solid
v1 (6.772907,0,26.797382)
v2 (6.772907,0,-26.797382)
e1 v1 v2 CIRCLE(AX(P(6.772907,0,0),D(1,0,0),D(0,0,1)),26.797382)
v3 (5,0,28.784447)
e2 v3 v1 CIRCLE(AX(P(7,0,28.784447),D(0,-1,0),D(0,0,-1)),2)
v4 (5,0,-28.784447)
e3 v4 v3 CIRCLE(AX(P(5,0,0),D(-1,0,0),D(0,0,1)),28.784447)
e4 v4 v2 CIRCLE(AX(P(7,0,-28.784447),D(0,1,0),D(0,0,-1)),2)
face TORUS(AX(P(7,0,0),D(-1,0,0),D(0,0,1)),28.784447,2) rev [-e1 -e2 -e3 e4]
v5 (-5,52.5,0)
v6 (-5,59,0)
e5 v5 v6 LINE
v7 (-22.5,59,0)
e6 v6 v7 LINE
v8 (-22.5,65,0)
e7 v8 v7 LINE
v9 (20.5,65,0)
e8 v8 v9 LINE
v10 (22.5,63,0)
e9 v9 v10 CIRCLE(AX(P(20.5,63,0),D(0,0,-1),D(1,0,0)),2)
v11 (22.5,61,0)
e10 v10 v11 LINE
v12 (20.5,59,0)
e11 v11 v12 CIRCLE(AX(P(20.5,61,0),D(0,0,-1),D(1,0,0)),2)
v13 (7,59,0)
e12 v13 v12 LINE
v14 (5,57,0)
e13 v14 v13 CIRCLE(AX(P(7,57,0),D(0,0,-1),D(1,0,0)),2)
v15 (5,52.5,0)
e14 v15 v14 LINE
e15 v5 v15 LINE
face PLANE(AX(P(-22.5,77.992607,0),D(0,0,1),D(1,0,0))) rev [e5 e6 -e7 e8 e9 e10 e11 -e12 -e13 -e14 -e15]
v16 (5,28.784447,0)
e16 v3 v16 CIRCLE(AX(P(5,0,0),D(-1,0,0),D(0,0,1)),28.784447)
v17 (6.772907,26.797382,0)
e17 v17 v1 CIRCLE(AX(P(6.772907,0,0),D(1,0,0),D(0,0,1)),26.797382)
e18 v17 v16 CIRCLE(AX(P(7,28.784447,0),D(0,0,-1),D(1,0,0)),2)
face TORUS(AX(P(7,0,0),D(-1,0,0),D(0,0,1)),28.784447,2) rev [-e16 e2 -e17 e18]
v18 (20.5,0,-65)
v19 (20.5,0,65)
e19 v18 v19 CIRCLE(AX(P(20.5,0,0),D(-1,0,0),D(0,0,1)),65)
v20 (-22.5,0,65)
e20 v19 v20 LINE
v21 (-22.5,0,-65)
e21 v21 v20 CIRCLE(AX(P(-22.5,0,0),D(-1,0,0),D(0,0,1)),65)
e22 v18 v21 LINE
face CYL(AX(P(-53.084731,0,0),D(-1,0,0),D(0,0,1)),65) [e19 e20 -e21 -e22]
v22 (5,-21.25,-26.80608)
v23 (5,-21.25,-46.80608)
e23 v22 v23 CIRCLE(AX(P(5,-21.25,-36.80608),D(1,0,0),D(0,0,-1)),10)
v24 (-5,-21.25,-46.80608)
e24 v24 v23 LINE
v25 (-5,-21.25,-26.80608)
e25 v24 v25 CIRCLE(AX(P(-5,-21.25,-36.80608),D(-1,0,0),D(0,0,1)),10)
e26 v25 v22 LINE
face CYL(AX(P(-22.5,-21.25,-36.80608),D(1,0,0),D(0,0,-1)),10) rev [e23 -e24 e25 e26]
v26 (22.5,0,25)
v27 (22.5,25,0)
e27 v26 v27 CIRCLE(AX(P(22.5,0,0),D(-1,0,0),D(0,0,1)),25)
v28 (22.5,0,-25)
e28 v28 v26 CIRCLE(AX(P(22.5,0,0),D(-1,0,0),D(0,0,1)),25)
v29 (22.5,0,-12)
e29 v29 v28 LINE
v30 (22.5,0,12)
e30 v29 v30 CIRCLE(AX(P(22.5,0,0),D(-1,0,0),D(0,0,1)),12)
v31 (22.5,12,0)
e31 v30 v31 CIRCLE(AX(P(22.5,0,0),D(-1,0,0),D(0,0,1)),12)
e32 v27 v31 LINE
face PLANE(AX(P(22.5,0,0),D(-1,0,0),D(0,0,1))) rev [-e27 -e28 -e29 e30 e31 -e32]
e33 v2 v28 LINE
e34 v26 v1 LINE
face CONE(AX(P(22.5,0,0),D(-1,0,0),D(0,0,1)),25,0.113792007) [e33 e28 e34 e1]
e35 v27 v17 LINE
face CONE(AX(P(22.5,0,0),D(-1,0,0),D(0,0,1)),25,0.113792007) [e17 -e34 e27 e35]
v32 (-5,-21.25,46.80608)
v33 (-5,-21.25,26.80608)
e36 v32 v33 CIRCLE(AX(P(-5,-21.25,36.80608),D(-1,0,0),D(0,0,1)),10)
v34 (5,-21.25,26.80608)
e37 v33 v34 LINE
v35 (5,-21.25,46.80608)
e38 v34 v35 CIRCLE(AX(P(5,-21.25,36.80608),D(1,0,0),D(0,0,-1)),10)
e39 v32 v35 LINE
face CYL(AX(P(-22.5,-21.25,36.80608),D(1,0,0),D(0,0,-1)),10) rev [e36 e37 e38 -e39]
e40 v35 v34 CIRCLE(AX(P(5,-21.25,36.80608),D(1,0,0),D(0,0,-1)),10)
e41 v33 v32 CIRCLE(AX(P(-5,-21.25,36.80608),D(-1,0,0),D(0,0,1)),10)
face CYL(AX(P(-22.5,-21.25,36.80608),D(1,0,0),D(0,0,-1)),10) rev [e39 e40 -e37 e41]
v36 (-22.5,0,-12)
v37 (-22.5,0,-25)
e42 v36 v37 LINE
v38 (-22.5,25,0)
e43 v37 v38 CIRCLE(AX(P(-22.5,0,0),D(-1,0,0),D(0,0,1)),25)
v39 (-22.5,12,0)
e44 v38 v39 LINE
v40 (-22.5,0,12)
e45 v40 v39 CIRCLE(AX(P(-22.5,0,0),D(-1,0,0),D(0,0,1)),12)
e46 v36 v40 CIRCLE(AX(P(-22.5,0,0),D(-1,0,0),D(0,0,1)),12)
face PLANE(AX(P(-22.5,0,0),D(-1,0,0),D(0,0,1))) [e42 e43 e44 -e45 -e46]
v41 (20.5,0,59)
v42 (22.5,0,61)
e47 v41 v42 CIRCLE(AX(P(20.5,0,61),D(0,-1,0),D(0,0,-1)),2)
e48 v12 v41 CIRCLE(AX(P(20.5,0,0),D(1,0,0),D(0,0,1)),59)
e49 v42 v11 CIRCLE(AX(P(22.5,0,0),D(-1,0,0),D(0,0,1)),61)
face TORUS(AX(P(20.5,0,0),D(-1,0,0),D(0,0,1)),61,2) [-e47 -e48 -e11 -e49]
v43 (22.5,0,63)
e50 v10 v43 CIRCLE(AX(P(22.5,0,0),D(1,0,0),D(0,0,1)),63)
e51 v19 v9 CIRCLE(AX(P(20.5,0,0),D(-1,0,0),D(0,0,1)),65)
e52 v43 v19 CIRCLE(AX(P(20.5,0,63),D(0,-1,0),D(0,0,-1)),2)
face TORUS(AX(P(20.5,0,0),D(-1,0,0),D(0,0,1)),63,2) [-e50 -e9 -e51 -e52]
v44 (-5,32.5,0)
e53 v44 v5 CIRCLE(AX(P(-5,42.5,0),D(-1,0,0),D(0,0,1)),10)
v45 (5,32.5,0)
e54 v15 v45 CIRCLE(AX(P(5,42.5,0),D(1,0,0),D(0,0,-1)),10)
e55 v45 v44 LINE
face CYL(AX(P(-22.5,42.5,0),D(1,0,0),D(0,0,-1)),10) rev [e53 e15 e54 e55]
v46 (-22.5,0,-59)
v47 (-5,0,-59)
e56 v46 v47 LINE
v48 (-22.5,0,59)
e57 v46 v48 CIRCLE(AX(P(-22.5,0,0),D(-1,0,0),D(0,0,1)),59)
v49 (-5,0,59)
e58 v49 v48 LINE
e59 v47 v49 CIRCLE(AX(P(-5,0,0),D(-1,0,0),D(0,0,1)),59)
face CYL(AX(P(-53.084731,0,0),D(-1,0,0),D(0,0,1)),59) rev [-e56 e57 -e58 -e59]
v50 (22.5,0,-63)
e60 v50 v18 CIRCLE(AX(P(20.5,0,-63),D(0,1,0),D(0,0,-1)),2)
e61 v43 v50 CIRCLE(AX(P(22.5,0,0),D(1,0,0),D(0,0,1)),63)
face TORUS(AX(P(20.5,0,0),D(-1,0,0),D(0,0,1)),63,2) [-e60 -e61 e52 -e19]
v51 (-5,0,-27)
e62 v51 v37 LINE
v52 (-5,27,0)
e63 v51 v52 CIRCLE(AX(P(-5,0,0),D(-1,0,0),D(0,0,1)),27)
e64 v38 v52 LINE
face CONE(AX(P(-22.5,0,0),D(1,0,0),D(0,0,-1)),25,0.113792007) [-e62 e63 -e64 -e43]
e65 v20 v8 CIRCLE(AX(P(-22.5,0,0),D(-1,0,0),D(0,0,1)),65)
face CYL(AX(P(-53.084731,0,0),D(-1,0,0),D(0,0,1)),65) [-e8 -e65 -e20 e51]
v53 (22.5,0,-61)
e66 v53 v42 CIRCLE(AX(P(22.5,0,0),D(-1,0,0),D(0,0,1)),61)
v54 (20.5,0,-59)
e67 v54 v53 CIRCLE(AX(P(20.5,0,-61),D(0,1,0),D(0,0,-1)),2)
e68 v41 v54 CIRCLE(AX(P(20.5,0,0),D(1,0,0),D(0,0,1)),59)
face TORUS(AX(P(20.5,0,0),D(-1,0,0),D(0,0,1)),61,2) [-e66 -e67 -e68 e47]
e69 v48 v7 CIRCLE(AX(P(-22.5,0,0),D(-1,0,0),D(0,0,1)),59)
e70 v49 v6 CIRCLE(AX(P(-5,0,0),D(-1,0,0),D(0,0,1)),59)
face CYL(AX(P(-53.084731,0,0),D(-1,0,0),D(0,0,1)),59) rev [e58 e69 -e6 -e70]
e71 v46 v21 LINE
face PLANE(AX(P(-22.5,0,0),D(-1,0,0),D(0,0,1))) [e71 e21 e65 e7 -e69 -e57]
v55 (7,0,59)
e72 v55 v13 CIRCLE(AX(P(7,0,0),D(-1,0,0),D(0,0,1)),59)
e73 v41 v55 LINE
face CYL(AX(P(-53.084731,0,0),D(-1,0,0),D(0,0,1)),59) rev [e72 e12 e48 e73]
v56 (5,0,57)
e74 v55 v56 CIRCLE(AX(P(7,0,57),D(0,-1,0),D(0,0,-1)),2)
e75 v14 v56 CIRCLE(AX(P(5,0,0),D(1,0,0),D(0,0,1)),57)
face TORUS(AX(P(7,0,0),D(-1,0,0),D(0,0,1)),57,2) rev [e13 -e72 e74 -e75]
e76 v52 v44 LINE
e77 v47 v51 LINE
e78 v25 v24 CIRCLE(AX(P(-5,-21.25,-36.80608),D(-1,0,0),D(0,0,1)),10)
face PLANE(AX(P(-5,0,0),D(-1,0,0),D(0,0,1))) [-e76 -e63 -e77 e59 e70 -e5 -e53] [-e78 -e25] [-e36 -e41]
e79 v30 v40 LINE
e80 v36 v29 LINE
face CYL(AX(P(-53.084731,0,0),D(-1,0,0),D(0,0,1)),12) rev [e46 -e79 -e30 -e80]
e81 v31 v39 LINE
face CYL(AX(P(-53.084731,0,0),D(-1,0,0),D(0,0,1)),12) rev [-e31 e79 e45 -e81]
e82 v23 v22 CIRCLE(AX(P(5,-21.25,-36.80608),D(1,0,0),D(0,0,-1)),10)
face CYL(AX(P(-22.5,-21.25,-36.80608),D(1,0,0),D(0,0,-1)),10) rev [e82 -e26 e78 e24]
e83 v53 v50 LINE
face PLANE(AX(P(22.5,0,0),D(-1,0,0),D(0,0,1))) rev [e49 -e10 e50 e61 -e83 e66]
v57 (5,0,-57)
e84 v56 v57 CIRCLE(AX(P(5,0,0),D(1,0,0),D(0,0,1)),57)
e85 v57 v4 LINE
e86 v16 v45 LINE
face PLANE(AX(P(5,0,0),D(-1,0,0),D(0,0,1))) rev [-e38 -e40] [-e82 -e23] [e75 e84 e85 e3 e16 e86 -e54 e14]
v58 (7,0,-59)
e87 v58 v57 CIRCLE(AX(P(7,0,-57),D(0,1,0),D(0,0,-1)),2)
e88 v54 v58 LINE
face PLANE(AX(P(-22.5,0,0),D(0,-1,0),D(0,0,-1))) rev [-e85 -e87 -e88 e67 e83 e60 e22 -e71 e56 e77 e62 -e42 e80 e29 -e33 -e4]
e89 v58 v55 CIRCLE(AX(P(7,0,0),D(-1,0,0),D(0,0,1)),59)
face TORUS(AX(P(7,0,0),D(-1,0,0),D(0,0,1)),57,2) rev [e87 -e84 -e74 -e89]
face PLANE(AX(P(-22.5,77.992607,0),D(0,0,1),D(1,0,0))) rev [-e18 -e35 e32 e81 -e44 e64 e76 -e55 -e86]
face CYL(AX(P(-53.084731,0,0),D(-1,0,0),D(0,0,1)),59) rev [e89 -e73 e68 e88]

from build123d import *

# Parameters (mm, degrees)
RIM_SLOT_SKETCH_R         = 10
RIM_SLOT_CUT_DEPTH        = 96.949205312
EDGE_FILLET_R2_A_R        = 2
EDGE_FILLET_R2_B_R        = 2
WEB_RELIEF_CUT_DEPTH      = 96.94920538
WEB_RELIEF_CUT_DEPTH_BACK = 96.94920538


with BuildPart() as part:
    # Wheel Profile Sketch → Wheel Body Revolve (revolve)
    with BuildSketch(Plane.XY, mode=Mode.PRIVATE) as wheel_body_revolve_sk:
        Polygon((22.5, 12), (-22.5, 12), (-22.5, 25), (-5, 27), (-5, 59), (-22.5, 59), (-22.5, 65), (22.5, 65), (22.5, 59), (5, 59), (5, 27), (22.5, 25), align=None)
    revolve(wheel_body_revolve_sk.sketch.rotate(Axis((-53.084730572, 0, 0), (1, 0, 0)), 90), axis=Axis((-53.084730572, 0, 0), (1, 0, 0)))

    # Rim Slot Sketch → Rim Slot Cut (cut, through all)
    with BuildSketch(Plane(origin=(5, 0, 0), x_dir=(0, 0, -1), z_dir=(1, 0, 0))):
        with Locations((0, 42.5)):
            Circle(RIM_SLOT_SKETCH_R)
        with Locations((36.806079661, -21.25)):
            Circle(RIM_SLOT_SKETCH_R)
        with Locations((-36.806079661, -21.25)):
            Circle(RIM_SLOT_SKETCH_R)
    extrude(amount=-RIM_SLOT_CUT_DEPTH, mode=Mode.SUBTRACT)

    # Edge Fillet R2 A
    edge_fillet_r2_a_edges = [part.edges().sort_by_distance(p)[0] for p in [
        (22.5, 0, -65),
        (5, 0, -59),
        (5, 0, -27),
    ]]
    fillet(edge_fillet_r2_a_edges, radius=EDGE_FILLET_R2_A_R)

    # Edge Fillet R2 B
    edge_fillet_r2_b_edges = [part.edges().sort_by_distance(p)[0] for p in [
        (22.5, 0, -59),
    ]]
    fillet(edge_fillet_r2_b_edges, radius=EDGE_FILLET_R2_B_R)

    # Web Relief Sketch → Web Relief Cut (cut, two sides: drawn at the far end of the back side and taken through both)
    with BuildSketch(Plane(origin=(5, 0, 0), x_dir=(0, 0, -1), z_dir=(1, 0, 0)).offset(-WEB_RELIEF_CUT_DEPTH_BACK)):
        with BuildLine():
            Line((0, 77.992606611), (0, 0))
            Line((0, 0), (85.280618665, 0))
            ThreePointArc((85.280618665, 0), (62.367801888, 60.567229614), (0, 77.992606611))
        make_face()
    extrude(amount=WEB_RELIEF_CUT_DEPTH + WEB_RELIEF_CUT_DEPTH_BACK, mode=Mode.SUBTRACT)


solid = part.part
